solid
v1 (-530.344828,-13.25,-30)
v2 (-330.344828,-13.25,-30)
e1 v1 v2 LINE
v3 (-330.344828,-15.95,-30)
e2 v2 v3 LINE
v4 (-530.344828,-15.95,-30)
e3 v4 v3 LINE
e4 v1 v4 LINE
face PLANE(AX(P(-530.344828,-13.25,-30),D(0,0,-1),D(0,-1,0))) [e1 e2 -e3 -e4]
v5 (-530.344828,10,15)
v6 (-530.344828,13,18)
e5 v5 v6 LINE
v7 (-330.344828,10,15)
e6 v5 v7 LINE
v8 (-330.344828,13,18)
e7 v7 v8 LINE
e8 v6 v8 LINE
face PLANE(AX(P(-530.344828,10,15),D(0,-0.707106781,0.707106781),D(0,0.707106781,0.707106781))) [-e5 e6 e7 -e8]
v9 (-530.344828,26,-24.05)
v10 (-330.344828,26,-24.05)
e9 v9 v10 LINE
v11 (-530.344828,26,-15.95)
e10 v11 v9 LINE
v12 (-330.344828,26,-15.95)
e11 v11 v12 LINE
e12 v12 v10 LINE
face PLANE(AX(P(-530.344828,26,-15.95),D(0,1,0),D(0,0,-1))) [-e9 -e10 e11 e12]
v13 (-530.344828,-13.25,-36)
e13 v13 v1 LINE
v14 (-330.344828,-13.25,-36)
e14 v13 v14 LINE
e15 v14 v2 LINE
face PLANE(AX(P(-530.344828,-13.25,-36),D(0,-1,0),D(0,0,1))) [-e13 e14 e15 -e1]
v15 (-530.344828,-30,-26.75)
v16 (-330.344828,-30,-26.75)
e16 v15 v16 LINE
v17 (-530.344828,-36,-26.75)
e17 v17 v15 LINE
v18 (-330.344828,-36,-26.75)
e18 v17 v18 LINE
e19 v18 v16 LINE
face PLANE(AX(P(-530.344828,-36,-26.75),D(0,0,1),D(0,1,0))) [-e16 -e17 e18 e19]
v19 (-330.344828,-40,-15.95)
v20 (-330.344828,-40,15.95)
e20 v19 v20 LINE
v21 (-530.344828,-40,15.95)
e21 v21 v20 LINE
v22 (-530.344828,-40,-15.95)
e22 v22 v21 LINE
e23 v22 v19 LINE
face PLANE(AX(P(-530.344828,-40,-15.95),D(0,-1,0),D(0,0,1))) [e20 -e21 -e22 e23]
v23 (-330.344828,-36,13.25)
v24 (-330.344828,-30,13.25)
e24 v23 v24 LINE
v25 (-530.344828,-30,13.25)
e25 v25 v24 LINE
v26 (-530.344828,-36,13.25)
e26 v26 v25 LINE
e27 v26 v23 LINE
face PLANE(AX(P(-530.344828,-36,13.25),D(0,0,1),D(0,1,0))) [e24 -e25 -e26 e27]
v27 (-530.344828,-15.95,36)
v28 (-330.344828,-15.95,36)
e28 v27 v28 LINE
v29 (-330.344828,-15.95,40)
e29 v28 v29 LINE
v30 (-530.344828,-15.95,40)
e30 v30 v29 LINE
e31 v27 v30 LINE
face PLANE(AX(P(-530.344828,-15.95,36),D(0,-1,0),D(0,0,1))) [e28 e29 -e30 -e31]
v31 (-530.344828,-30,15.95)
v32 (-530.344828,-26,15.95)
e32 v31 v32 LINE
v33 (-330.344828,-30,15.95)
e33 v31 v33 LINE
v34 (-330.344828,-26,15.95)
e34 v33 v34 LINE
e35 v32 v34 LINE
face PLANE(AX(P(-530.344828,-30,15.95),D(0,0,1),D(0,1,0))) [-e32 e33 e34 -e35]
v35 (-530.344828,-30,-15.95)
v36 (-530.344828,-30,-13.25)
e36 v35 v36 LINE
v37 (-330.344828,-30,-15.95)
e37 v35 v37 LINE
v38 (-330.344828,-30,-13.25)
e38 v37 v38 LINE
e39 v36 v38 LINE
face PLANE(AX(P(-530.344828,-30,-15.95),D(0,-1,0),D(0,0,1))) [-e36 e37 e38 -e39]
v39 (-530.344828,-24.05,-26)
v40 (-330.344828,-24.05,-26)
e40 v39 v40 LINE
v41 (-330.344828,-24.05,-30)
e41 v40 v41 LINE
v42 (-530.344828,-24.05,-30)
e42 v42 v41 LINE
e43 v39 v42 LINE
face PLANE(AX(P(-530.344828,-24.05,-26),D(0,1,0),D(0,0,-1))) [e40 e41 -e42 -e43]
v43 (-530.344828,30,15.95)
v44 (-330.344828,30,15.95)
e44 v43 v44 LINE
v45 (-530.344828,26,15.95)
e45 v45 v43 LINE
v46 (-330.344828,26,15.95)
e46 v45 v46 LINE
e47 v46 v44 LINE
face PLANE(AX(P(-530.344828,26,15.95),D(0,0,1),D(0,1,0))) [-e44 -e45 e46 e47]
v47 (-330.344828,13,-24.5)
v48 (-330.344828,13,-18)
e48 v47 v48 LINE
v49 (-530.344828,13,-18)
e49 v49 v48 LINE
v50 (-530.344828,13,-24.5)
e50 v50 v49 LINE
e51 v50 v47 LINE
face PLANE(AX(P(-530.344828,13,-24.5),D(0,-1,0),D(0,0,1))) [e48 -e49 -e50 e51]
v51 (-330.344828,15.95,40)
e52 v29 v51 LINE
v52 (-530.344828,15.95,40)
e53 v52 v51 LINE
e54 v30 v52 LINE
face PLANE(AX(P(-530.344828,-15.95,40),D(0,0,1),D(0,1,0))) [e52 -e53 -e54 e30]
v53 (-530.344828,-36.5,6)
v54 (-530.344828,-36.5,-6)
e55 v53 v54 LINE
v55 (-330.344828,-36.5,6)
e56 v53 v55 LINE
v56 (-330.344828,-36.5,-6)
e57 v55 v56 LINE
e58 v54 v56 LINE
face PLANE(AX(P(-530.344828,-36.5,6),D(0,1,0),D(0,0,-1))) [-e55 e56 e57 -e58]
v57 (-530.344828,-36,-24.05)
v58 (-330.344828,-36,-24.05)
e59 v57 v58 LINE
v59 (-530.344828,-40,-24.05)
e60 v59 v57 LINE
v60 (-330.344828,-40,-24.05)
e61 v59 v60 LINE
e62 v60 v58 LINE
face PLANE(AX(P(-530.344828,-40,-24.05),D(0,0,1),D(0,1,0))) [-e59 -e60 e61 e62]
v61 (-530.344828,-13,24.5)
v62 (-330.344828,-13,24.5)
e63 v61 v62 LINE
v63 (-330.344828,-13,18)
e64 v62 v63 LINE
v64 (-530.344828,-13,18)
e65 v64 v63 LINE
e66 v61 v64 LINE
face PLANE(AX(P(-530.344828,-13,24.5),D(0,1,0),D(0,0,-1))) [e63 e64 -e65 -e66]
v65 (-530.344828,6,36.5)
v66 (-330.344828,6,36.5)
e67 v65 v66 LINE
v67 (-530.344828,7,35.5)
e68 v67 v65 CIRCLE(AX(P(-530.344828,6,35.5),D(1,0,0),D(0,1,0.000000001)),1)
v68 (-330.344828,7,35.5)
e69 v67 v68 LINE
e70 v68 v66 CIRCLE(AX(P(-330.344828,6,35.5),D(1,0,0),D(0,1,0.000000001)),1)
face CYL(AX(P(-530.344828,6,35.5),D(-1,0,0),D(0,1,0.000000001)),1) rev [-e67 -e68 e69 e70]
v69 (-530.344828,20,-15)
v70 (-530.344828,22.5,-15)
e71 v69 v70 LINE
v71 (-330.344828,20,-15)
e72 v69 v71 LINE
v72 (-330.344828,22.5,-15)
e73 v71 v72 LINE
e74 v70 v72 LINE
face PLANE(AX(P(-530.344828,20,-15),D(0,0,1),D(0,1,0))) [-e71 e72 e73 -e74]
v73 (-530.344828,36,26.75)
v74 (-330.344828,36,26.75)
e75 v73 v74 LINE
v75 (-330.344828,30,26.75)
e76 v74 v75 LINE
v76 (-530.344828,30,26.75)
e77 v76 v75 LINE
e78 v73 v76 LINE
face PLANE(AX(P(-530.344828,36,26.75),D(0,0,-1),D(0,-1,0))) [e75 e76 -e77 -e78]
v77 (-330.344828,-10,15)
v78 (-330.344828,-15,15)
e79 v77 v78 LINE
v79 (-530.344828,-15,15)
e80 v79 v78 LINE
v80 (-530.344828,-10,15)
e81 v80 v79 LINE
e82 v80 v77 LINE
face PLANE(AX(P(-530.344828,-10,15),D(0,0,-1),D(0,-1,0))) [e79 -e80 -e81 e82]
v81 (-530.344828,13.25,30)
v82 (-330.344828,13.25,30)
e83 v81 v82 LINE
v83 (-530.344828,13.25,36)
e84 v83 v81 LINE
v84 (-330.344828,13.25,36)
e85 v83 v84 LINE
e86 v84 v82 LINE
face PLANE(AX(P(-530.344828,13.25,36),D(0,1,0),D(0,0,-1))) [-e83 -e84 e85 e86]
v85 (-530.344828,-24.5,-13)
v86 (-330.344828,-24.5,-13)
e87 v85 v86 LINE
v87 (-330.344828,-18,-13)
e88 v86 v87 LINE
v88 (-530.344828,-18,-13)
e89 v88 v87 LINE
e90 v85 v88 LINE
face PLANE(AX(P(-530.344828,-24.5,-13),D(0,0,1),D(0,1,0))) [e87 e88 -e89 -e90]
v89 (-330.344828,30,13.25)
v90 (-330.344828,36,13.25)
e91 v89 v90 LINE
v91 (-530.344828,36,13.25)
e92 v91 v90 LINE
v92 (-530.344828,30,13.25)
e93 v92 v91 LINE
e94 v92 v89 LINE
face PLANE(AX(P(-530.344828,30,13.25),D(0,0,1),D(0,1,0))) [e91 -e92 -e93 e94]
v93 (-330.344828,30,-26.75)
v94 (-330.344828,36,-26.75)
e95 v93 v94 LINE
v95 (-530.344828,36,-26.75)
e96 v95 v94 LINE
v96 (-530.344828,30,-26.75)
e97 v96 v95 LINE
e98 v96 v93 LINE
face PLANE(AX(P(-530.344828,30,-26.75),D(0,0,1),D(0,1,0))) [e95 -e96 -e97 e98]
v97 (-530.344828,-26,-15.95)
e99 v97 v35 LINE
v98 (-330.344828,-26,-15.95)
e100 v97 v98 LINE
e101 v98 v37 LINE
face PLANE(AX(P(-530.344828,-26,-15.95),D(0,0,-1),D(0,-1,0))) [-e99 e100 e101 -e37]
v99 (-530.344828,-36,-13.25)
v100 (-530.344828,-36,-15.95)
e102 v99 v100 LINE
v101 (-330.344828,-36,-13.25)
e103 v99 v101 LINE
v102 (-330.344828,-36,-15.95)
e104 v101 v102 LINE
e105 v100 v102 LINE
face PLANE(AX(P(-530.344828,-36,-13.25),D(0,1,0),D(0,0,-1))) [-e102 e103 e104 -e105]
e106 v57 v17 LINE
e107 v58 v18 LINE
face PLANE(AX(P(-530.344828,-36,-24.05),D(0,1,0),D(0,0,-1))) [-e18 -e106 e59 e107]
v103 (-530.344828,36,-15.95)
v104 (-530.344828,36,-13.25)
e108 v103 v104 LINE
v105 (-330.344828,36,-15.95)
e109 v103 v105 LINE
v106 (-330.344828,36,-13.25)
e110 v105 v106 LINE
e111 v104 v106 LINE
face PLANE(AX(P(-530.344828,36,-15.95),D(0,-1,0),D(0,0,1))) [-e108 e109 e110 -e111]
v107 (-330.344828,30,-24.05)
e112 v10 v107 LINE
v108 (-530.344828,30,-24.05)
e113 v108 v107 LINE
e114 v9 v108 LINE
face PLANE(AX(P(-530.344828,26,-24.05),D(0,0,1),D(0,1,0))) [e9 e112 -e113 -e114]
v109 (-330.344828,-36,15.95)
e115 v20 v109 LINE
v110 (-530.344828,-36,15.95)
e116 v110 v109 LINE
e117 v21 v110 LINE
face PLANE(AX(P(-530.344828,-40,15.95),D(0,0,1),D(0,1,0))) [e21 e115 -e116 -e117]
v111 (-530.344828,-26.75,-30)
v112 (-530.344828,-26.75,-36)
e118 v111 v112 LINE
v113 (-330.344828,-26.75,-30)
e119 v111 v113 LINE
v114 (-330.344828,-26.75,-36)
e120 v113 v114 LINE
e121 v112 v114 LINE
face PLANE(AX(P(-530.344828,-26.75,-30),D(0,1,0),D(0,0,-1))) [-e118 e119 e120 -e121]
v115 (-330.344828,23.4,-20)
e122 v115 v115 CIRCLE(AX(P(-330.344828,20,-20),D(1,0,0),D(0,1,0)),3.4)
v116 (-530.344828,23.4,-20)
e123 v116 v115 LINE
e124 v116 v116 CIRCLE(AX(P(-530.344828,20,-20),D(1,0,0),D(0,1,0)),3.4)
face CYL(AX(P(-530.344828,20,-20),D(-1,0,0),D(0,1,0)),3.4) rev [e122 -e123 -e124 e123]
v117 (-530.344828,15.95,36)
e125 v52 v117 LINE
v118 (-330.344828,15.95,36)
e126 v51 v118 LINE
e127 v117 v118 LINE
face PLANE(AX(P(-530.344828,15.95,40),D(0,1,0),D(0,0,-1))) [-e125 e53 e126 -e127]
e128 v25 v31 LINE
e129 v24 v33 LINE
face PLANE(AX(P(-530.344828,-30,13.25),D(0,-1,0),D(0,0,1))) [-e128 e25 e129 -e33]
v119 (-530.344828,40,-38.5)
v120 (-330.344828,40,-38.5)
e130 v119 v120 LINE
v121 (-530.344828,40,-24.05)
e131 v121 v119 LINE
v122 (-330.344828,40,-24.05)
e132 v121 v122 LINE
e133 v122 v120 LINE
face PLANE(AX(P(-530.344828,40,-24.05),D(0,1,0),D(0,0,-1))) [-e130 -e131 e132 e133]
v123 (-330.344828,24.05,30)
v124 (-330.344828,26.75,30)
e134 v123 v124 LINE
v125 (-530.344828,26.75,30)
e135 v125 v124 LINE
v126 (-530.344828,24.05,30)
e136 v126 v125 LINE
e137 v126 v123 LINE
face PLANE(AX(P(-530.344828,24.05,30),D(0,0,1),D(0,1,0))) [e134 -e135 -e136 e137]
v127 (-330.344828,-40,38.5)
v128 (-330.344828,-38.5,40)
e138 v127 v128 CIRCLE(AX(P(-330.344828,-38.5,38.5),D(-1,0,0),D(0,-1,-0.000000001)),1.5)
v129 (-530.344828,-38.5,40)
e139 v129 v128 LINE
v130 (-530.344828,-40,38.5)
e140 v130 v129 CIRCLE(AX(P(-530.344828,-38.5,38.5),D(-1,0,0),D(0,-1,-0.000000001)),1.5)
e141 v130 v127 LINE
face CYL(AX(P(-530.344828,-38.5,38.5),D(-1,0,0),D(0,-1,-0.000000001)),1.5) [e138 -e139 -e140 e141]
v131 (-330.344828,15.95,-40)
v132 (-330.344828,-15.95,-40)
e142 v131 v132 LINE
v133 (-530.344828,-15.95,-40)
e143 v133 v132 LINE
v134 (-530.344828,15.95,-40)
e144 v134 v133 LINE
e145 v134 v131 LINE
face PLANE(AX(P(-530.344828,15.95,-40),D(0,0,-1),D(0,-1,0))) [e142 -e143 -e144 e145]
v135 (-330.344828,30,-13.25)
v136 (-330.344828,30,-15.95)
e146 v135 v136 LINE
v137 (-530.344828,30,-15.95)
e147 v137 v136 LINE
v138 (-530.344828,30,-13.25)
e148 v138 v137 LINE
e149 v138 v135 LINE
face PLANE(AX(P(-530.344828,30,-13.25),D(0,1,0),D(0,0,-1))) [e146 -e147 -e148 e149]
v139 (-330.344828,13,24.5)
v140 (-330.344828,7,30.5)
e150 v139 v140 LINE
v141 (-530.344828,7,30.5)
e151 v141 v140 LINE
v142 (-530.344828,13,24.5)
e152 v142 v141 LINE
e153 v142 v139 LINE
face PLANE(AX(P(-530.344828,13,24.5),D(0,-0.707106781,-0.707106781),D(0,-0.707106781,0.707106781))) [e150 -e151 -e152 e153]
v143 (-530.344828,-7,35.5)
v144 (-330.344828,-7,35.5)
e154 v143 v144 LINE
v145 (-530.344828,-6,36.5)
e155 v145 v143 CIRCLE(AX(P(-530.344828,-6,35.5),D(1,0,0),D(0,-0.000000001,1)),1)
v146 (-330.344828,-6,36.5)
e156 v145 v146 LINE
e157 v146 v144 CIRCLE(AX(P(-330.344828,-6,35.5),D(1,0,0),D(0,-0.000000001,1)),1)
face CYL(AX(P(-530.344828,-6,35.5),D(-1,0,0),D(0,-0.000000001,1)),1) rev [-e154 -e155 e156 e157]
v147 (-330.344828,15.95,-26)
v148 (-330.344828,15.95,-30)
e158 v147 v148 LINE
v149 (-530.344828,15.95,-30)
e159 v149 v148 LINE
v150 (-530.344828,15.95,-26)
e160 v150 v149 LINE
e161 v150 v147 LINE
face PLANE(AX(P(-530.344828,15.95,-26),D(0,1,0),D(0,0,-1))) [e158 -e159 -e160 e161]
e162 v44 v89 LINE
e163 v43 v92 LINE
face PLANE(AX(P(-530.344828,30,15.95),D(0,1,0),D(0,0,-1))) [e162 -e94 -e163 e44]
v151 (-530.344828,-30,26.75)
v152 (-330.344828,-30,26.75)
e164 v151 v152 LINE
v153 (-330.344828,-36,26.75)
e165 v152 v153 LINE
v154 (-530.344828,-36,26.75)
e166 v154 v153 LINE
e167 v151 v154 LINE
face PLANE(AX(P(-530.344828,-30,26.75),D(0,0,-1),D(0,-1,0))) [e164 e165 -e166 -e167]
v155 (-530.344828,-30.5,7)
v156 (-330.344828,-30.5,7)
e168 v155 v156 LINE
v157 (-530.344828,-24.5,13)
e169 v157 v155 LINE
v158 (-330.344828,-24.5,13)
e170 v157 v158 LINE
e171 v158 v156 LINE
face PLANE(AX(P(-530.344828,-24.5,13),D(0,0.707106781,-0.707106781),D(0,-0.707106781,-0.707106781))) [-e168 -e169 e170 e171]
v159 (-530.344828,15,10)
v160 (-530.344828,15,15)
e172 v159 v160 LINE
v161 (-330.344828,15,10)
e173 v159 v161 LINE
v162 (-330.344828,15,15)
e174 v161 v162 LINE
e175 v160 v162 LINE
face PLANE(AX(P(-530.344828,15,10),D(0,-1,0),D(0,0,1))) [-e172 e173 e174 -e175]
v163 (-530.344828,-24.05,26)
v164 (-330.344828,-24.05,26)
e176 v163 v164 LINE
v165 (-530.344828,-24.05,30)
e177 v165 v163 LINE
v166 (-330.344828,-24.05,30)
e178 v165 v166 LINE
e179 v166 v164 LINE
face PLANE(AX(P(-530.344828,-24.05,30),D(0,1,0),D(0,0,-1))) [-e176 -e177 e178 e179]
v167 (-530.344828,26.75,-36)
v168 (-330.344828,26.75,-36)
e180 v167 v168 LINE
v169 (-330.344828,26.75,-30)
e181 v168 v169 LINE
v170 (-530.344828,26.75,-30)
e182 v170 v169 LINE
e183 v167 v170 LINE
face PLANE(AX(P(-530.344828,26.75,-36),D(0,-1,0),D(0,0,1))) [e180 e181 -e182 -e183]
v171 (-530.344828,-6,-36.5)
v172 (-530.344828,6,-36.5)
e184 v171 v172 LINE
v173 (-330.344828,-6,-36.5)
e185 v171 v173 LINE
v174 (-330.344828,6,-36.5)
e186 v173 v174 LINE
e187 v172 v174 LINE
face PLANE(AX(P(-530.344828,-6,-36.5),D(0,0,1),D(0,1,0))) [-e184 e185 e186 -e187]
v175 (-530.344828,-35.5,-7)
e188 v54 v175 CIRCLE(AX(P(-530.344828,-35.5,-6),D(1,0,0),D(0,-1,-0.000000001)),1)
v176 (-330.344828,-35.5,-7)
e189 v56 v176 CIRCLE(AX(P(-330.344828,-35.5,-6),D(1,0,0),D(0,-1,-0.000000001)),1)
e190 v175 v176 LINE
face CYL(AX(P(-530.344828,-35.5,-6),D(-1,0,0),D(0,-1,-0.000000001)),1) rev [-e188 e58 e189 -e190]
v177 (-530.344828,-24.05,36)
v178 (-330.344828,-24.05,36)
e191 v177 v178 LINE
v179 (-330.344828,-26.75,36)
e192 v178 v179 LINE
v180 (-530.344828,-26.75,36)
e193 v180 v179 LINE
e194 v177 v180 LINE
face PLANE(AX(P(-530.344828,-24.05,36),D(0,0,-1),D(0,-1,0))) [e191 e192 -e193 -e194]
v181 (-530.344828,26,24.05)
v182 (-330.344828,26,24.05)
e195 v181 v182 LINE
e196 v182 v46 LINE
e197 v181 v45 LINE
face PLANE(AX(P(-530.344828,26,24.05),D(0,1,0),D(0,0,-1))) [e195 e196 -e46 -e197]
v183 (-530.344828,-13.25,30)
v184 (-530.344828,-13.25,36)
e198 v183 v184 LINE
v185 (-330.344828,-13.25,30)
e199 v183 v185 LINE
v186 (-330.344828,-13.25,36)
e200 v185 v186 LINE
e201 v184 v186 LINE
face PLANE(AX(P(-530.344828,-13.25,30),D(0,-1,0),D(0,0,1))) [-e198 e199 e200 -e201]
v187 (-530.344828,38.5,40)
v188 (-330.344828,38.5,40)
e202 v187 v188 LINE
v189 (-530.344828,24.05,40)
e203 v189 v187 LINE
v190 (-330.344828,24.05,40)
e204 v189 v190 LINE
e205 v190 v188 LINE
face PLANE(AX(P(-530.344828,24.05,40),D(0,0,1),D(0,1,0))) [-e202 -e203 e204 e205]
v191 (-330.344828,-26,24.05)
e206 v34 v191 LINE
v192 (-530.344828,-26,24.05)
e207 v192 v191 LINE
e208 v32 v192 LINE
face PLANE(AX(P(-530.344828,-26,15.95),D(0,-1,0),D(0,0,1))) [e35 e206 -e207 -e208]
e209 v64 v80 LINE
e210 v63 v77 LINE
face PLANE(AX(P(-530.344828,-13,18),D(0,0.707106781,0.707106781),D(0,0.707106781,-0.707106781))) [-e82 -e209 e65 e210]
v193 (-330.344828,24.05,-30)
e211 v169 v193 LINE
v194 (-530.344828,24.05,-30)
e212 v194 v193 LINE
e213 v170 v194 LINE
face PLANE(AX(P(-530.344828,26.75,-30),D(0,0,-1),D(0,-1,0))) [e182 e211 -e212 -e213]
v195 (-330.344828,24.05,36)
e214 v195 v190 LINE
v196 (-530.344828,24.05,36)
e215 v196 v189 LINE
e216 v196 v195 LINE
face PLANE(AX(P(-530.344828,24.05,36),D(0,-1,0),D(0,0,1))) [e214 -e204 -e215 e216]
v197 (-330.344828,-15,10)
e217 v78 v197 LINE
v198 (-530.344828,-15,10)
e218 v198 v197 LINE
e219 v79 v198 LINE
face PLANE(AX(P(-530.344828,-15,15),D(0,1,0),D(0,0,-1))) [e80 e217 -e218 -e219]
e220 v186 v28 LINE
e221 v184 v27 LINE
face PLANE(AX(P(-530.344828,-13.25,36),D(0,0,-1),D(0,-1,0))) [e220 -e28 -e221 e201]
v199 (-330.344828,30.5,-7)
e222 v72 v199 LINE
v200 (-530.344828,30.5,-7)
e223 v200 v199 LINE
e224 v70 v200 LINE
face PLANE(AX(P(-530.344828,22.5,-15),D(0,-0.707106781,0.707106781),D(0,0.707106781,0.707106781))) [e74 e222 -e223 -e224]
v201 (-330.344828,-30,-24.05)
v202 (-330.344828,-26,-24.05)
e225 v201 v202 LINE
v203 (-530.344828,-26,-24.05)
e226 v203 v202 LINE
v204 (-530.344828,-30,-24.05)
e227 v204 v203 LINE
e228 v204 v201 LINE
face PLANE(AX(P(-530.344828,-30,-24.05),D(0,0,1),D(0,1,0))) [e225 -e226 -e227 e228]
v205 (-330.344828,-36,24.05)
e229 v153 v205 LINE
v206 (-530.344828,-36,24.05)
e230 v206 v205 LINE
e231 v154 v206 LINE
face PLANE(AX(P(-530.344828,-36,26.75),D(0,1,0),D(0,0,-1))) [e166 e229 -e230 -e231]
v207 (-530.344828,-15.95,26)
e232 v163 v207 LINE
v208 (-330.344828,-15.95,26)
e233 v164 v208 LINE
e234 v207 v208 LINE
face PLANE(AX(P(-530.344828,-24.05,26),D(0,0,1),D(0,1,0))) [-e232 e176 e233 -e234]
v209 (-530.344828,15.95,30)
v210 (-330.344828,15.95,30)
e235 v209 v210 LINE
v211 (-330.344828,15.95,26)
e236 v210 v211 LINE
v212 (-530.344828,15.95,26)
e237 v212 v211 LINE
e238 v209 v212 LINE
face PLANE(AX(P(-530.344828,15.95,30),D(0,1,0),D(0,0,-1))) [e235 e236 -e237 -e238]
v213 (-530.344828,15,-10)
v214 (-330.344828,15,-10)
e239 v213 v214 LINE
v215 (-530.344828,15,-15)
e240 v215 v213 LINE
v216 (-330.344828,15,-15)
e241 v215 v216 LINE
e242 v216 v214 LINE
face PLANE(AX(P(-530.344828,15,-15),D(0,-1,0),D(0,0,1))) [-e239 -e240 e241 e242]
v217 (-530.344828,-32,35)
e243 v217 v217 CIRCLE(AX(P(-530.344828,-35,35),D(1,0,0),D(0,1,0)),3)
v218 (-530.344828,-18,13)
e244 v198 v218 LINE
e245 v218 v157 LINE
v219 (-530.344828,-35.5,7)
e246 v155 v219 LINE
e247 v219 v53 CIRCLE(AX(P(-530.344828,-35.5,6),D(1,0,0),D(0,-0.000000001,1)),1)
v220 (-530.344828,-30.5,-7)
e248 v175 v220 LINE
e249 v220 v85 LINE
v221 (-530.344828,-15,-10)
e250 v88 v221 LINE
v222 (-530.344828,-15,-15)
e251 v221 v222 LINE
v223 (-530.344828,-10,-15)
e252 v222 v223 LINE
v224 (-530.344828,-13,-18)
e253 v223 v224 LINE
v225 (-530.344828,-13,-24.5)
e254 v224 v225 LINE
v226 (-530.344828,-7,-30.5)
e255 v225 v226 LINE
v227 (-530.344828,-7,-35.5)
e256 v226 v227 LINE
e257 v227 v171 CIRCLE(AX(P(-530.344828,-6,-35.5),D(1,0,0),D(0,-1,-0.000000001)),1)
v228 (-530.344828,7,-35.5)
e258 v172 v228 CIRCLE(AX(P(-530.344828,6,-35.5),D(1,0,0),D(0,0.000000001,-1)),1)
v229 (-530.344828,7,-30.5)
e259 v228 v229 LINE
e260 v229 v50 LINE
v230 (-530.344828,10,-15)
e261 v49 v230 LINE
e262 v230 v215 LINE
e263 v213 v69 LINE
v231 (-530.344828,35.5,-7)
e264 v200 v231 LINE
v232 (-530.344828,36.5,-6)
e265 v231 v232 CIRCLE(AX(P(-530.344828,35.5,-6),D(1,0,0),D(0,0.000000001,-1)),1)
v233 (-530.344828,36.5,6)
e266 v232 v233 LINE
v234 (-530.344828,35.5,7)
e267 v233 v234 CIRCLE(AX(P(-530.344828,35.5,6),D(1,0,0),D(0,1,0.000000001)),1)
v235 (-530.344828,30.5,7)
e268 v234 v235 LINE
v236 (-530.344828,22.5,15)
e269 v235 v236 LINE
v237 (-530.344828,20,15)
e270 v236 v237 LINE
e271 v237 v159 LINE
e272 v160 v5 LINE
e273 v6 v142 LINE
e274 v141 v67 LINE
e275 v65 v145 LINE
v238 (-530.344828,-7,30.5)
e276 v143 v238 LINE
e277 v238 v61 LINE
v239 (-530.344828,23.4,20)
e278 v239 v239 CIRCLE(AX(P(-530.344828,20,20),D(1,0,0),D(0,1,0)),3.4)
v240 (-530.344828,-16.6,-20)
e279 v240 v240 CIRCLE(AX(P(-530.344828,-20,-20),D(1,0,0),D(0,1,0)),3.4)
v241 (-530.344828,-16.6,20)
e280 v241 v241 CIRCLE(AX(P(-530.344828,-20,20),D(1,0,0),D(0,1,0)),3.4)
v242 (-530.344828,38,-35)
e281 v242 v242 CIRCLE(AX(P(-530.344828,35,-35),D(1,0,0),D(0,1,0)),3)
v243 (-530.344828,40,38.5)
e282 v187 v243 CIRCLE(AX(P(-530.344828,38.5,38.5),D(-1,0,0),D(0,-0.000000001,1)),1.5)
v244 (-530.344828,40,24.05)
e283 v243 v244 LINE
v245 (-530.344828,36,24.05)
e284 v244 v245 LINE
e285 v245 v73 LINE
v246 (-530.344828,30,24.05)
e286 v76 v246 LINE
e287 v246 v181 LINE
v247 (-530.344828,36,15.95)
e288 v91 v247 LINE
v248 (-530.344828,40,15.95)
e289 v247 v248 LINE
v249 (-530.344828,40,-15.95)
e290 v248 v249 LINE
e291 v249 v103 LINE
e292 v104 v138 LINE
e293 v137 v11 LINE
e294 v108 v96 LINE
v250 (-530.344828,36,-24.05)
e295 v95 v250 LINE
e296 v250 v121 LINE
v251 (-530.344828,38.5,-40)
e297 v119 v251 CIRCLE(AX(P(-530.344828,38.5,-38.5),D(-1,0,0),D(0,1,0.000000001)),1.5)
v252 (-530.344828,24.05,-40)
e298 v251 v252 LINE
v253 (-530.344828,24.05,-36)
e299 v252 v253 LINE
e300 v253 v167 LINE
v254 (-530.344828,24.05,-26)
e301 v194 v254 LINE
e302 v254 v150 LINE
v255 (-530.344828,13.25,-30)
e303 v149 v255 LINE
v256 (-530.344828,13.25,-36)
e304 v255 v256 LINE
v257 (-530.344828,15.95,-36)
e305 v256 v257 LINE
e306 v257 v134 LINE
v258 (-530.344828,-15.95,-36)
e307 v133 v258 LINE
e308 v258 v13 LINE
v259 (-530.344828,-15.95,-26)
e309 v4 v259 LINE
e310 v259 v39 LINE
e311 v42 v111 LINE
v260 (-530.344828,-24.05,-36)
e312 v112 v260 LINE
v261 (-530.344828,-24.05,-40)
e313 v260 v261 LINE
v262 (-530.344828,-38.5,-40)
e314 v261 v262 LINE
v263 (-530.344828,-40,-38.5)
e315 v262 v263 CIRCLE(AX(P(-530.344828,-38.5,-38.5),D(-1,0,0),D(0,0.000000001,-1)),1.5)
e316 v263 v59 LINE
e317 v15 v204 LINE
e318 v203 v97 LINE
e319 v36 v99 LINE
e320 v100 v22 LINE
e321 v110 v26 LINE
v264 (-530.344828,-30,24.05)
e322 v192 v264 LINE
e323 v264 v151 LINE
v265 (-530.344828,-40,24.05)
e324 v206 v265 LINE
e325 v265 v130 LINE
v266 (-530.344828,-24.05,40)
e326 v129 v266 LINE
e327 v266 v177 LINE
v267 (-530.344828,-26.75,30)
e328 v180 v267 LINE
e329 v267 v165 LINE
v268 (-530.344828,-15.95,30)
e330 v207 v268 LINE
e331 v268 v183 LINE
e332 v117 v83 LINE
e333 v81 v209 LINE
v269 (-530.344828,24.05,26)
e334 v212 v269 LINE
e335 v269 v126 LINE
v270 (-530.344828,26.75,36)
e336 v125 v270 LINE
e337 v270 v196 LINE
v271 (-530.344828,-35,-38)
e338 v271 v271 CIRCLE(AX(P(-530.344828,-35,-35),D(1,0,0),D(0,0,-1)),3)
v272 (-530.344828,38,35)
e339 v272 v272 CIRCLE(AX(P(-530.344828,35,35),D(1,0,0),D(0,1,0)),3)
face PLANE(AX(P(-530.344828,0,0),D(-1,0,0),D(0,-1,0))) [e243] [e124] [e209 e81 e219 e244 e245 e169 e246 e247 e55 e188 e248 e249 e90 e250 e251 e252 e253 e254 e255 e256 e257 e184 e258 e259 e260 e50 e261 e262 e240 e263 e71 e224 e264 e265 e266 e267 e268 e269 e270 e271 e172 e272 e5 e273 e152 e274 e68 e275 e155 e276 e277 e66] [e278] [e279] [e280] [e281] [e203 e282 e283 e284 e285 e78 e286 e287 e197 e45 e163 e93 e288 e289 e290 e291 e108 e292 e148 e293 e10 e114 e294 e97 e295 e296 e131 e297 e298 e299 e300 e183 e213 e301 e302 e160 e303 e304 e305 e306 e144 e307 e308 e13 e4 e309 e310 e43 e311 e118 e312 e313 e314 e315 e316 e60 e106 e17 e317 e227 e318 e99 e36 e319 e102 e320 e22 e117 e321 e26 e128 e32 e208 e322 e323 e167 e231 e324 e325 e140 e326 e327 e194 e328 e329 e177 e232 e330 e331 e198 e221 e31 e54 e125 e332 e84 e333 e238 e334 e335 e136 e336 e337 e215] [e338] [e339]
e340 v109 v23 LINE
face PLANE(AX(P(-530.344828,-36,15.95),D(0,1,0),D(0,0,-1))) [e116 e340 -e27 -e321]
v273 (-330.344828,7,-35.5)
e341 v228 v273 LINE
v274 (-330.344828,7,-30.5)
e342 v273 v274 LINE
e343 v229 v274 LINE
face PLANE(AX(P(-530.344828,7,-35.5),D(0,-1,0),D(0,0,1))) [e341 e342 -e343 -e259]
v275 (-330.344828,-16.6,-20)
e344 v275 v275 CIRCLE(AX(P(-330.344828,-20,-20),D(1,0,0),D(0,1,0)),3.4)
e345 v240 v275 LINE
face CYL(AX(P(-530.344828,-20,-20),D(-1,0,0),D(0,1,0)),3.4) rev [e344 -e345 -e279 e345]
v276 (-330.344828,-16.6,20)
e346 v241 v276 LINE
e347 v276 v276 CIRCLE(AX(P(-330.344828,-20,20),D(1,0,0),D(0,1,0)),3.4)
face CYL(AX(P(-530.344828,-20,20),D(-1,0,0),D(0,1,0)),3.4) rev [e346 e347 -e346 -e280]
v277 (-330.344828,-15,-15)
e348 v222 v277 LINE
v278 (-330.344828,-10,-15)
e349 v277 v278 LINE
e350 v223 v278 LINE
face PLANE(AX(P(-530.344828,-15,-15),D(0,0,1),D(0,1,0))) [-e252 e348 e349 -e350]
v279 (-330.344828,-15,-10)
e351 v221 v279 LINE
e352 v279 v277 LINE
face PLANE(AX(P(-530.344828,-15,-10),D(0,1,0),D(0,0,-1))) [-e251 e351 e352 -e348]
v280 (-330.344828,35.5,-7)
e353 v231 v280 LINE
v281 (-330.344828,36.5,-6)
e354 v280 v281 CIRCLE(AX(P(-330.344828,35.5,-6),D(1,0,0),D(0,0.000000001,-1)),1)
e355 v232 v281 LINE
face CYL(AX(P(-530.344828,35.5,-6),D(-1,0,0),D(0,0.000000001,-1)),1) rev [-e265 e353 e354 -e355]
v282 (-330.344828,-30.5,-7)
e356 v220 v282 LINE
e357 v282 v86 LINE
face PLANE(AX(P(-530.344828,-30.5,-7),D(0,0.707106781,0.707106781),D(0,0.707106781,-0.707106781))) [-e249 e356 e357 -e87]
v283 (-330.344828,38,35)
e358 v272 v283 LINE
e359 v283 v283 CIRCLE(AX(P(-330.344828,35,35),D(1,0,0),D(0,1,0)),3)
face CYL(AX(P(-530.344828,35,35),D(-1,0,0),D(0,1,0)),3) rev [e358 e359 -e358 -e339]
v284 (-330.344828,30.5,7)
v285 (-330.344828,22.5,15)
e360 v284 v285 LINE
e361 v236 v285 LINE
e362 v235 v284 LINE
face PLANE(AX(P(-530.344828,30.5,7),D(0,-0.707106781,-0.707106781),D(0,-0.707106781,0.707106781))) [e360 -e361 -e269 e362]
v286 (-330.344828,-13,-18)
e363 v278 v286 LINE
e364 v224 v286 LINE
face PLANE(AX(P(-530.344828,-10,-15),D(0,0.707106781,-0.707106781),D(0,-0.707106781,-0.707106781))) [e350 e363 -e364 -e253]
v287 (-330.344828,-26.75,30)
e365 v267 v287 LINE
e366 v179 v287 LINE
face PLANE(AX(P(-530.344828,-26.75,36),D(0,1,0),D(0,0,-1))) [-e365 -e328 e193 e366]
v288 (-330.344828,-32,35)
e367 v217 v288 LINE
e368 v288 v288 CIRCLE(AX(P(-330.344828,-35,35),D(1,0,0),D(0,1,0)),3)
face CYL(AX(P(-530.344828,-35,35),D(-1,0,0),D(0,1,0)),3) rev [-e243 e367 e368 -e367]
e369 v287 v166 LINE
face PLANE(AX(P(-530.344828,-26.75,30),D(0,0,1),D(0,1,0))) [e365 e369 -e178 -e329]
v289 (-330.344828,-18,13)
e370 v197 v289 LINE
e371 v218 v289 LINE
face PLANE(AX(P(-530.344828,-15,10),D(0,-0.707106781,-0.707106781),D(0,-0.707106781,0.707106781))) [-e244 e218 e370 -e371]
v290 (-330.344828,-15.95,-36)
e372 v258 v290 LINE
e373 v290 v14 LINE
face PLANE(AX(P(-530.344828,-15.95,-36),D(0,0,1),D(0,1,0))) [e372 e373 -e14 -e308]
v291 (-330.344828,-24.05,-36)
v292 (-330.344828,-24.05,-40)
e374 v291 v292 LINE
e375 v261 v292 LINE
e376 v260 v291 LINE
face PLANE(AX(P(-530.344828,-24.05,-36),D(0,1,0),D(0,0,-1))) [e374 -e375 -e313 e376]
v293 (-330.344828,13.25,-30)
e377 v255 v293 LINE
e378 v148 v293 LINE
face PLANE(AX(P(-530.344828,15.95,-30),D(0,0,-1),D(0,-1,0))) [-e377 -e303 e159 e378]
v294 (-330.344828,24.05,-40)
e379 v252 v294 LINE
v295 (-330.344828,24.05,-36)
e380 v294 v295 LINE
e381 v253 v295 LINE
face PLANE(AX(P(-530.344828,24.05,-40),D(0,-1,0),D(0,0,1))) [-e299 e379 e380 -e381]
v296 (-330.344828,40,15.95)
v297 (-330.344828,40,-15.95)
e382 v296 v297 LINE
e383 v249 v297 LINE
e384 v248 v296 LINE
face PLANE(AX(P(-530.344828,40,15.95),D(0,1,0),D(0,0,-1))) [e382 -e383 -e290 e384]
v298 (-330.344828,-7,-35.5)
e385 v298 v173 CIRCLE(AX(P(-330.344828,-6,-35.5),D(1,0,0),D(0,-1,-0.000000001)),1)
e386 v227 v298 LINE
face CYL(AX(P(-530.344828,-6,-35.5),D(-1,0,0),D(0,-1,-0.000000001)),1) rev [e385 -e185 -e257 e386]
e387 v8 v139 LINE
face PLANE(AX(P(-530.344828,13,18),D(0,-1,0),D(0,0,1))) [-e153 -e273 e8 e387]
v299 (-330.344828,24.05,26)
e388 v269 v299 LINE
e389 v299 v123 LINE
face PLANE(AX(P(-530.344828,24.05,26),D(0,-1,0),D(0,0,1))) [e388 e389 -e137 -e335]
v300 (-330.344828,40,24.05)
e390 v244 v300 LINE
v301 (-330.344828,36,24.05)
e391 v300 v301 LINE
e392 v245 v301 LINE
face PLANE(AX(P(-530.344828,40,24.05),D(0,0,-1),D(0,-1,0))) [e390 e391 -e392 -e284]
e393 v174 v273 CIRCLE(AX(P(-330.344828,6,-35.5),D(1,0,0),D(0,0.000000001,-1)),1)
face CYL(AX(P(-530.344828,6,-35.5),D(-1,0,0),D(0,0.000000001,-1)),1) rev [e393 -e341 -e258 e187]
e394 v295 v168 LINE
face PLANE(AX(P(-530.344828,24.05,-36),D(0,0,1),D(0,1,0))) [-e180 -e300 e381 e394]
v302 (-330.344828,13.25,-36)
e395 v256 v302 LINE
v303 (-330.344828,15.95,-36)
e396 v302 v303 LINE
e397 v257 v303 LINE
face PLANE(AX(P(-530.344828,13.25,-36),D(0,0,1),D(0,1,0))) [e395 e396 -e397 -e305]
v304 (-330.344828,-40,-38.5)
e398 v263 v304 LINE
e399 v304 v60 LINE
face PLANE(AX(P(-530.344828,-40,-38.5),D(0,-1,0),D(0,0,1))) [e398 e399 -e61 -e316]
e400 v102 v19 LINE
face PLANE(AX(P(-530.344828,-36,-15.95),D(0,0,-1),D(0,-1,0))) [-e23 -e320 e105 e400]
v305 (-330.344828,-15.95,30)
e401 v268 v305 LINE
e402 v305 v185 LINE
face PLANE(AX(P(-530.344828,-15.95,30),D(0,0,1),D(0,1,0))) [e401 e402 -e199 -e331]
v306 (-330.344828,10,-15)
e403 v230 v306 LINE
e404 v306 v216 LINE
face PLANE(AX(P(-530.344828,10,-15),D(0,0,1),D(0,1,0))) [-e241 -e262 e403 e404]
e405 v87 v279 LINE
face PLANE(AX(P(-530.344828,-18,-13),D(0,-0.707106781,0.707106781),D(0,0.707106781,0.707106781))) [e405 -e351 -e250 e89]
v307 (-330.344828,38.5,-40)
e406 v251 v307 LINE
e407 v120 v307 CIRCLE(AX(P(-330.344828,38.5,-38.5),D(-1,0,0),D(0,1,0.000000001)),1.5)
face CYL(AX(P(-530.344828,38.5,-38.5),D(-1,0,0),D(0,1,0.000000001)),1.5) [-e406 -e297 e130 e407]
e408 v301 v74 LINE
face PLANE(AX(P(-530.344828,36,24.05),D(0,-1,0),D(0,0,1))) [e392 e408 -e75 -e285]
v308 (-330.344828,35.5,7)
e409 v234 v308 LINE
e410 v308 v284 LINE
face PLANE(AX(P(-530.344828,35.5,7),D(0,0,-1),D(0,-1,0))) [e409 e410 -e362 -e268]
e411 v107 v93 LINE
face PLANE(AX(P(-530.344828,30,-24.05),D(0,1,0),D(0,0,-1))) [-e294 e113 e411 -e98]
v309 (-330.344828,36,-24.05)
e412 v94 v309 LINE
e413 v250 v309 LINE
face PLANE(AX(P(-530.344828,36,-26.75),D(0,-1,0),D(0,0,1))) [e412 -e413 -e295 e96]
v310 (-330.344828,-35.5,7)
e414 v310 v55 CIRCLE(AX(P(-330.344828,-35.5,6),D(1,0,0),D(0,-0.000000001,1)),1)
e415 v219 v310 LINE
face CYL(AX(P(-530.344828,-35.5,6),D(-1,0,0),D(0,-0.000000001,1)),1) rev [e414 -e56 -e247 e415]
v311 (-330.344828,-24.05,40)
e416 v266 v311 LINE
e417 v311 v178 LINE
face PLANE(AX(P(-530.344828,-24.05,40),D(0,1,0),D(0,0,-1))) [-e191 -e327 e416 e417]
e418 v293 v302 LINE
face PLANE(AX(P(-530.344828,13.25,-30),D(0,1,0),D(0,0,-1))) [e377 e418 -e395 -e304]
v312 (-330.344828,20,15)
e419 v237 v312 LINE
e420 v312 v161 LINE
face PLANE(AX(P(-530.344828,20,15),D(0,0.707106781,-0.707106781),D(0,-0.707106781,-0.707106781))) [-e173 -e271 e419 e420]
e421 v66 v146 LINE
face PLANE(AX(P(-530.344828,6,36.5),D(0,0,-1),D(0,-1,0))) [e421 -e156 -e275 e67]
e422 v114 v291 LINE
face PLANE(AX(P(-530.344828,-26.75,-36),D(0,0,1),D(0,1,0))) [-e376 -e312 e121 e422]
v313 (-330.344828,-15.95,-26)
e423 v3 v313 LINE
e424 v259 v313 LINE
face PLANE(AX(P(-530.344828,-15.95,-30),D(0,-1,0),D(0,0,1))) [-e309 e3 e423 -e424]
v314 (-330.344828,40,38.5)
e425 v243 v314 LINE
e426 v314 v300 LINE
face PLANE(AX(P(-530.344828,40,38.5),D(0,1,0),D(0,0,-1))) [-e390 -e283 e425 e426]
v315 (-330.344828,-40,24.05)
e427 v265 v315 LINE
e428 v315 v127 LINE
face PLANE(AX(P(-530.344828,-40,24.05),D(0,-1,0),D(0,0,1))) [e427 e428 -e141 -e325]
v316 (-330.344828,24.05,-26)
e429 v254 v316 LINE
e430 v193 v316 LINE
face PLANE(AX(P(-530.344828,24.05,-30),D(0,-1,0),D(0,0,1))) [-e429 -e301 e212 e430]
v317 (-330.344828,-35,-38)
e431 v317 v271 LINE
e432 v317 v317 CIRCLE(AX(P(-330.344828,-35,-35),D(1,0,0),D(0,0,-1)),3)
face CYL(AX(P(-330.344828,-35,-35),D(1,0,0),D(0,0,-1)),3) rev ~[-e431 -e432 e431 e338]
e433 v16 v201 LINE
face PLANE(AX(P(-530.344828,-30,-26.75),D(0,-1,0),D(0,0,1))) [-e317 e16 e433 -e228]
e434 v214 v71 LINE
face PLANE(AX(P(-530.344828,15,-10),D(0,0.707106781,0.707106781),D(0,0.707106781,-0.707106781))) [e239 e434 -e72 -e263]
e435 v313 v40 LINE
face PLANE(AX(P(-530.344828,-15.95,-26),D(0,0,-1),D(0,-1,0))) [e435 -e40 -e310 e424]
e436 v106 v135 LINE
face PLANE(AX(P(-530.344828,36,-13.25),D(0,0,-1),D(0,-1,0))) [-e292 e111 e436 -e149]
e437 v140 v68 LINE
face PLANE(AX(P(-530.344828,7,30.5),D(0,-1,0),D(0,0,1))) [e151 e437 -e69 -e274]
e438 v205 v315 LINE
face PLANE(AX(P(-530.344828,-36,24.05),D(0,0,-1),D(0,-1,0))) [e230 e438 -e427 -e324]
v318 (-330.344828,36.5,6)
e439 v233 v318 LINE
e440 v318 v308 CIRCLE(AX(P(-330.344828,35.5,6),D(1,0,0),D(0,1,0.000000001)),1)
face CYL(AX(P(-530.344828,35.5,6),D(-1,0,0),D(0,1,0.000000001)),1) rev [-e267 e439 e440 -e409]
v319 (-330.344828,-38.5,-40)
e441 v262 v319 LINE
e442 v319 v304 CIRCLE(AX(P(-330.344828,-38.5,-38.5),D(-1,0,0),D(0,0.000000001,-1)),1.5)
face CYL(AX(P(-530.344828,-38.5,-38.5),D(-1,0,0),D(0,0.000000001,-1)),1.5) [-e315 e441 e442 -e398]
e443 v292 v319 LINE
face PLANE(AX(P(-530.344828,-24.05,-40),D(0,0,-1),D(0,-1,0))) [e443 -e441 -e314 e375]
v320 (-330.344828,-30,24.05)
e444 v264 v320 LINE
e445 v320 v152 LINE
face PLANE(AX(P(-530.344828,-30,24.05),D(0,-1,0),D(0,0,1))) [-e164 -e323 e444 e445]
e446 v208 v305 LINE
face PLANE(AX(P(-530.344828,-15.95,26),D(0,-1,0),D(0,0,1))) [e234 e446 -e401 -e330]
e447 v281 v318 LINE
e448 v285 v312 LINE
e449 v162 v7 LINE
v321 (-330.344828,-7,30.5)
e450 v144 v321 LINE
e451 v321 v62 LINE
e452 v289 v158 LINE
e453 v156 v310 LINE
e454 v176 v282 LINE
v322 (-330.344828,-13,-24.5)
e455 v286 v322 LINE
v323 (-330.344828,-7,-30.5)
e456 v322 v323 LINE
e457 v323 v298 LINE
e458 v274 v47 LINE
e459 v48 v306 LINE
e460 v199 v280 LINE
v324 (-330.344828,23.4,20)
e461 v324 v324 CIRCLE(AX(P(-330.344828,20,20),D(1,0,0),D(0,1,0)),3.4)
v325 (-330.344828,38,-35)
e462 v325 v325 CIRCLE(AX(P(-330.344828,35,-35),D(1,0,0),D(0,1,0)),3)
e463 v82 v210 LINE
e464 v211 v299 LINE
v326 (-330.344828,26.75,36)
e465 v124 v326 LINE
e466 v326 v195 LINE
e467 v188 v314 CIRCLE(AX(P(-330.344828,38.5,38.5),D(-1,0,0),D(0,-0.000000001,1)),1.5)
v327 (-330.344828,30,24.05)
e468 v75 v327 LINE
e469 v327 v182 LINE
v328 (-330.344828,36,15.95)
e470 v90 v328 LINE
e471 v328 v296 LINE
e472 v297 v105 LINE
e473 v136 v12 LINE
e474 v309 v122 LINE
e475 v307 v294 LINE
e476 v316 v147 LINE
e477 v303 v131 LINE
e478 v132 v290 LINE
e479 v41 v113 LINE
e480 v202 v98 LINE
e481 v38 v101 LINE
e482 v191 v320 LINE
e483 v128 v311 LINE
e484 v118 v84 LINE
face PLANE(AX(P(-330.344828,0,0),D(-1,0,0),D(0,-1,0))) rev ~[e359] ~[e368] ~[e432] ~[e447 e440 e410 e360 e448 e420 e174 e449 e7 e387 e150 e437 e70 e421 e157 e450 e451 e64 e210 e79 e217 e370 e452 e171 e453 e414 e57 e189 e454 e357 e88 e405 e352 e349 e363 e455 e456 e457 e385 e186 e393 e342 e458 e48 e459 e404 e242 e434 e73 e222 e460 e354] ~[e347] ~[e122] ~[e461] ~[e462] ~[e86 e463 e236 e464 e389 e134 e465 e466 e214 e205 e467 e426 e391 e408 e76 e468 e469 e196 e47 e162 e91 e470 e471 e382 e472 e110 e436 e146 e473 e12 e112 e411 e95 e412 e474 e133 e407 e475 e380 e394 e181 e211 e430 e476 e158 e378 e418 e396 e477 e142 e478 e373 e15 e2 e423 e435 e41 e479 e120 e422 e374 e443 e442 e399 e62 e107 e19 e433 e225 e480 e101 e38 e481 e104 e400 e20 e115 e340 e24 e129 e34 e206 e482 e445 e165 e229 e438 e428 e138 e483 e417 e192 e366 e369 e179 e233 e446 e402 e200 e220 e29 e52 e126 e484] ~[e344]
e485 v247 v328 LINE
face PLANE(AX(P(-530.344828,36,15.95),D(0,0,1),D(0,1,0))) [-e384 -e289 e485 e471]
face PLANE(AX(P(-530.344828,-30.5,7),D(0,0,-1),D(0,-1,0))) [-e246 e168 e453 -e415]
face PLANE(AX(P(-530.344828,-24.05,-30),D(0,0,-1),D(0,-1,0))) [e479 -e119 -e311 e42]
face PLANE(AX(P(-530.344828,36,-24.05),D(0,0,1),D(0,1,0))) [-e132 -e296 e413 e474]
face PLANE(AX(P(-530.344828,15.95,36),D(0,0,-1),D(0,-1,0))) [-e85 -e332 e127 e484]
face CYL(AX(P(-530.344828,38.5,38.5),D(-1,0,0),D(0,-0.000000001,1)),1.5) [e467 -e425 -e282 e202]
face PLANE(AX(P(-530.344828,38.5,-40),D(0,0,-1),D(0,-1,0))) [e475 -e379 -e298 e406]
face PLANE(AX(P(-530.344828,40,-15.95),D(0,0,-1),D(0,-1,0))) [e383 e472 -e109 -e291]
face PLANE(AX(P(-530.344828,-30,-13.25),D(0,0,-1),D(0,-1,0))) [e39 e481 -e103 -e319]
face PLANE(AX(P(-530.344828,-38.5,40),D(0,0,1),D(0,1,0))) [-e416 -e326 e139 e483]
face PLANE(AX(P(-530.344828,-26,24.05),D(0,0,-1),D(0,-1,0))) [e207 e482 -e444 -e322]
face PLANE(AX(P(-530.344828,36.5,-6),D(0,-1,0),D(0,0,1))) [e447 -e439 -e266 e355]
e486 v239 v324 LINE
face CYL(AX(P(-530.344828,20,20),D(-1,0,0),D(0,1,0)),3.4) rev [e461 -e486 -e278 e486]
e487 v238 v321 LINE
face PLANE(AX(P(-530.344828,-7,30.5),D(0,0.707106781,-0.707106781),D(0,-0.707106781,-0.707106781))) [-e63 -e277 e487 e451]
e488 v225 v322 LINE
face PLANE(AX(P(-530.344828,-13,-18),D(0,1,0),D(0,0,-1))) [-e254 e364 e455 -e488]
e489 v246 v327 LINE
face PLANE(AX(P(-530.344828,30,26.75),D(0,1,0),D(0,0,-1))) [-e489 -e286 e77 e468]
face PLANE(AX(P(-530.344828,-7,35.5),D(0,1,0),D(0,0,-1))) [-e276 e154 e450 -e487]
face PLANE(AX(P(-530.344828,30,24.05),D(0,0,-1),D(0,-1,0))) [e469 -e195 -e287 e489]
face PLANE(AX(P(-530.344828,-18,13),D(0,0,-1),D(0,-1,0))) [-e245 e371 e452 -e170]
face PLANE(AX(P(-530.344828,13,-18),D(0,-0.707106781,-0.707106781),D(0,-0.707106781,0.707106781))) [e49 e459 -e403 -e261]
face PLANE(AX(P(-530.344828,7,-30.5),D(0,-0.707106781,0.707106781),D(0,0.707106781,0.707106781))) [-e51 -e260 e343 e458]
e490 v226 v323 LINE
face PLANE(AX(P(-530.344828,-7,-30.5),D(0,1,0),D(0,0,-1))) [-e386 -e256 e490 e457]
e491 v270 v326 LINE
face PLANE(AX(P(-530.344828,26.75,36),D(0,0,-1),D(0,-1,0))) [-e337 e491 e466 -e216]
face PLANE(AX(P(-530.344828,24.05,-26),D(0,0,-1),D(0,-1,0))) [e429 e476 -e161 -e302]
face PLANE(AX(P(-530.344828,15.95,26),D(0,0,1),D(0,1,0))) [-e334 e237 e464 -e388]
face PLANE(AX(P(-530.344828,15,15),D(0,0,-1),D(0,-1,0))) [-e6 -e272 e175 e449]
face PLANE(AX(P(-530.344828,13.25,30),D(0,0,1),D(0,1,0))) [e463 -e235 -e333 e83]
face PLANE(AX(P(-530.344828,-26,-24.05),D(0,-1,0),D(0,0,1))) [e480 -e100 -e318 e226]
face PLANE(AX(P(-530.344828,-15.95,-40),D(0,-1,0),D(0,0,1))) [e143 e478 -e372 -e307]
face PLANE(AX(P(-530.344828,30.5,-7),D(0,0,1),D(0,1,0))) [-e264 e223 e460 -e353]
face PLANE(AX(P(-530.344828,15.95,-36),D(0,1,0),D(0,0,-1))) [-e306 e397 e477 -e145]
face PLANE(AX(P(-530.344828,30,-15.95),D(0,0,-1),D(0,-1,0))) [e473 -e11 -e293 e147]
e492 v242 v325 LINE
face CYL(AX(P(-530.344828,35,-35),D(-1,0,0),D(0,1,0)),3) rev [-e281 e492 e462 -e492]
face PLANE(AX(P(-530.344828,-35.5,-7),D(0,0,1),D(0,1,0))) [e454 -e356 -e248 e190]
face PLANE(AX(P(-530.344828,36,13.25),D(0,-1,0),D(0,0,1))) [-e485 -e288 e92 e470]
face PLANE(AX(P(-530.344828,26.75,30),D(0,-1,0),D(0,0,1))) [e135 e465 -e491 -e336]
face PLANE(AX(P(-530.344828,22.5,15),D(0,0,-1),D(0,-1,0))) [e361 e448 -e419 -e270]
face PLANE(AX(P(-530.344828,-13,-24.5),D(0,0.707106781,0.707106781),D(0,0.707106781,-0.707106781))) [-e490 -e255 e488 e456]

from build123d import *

# Parameters (mm, degrees)
SKETCH1_R                                 = 3.4
SKETCH1_R_2                               = 3
ALUMINIUM_PROFILE_80_X_80G_X_R1_5_1_DEPTH = 200
SKETCH10_R                                = 3
CUT_EXTRUDE1_DEPTH                        = 208.846096908


with BuildPart() as part:
    # Sketch1 → Aluminium profile 80 X 80G X R1.5(1) (new body)
    with BuildSketch(Plane.YZ.offset(-530.344827586)):
        with BuildLine():
            Line((-24.05, 40), (-24.05, 36))
            Line((-24.05, 36), (-26.75, 36))
            Line((-26.75, 36), (-26.75, 30))
            Line((-26.75, 30), (-24.05, 30))
            Line((-24.05, 30), (-24.05, 26))
            Line((-24.05, 26), (-15.95, 26))
            Line((-15.95, 26), (-15.95, 30))
            Line((-15.95, 30), (-13.25, 30))
            Line((-13.25, 30), (-13.25, 36))
            Line((-13.25, 36), (-15.95, 36))
            Line((-15.95, 36), (-15.95, 40))
            Line((-15.95, 40), (15.95, 40))
            Line((15.95, 40), (15.95, 36))
            Line((15.95, 36), (13.25, 36))
            Line((13.25, 36), (13.25, 30))
            Line((13.25, 30), (15.95, 30))
            Line((15.95, 30), (15.95, 26))
            Line((15.95, 26), (24.05, 26))
            Line((24.05, 26), (24.05, 30))
            Line((24.05, 30), (26.75, 30))
            Line((26.75, 30), (26.75, 36))
            Line((26.75, 36), (24.05, 36))
            Line((24.05, 36), (24.05, 40))
            Line((24.05, 40), (38.5, 40))
            ThreePointArc((38.5, 40), (39.560660172, 39.560660172), (40, 38.5))
            Line((40, 38.5), (40, 24.05))
            Line((40, 24.05), (36, 24.05))
            Line((36, 24.05), (36, 26.75))
            Line((36, 26.75), (30, 26.75))
            Line((30, 26.75), (30, 24.05))
            Line((30, 24.05), (26, 24.05))
            Line((26, 24.05), (26, 15.95))
            Line((26, 15.95), (30, 15.95))
            Line((30, 15.95), (30, 13.25))
            Line((30, 13.25), (36, 13.25))
            Line((36, 13.25), (36, 15.95))
            Line((36, 15.95), (40, 15.95))
            Line((40, 15.95), (40, -15.95))
            Line((40, -15.95), (36, -15.95))
            Line((36, -15.95), (36, -13.25))
            Line((36, -13.25), (30, -13.25))
            Line((30, -13.25), (30, -15.95))
            Line((30, -15.95), (26, -15.95))
            Line((26, -15.95), (26, -24.05))
            Line((26, -24.05), (30, -24.05))
            Line((30, -24.05), (30, -26.75))
            Line((30, -26.75), (36, -26.75))
            Line((36, -26.75), (36, -24.05))
            Line((36, -24.05), (40, -24.05))
            Line((40, -24.05), (40, -38.5))
            ThreePointArc((40, -38.5), (39.560660172, -39.560660172), (38.5, -40))
            Line((38.5, -40), (24.05, -40))
            Line((24.05, -40), (24.05, -36))
            Line((24.05, -36), (26.75, -36))
            Line((26.75, -36), (26.75, -30))
            Line((26.75, -30), (24.05, -30))
            Line((24.05, -30), (24.05, -26))
            Line((24.05, -26), (15.95, -26))
            Line((15.95, -26), (15.95, -30))
            Line((15.95, -30), (13.25, -30))
            Line((13.25, -30), (13.25, -36))
            Line((13.25, -36), (15.95, -36))
            Line((15.95, -36), (15.95, -40))
            Line((15.95, -40), (-15.95, -40))
            Line((-15.95, -40), (-15.95, -36))
            Line((-15.95, -36), (-13.25, -36))
            Line((-13.25, -36), (-13.25, -30))
            Line((-13.25, -30), (-15.95, -30))
            Line((-15.95, -30), (-15.95, -26))
            Line((-15.95, -26), (-24.05, -26))
            Line((-24.05, -26), (-24.05, -30))
            Line((-24.05, -30), (-26.75, -30))
            Line((-26.75, -30), (-26.75, -36))
            Line((-26.75, -36), (-24.05, -36))
            Line((-24.05, -36), (-24.05, -40))
            Line((-24.05, -40), (-38.5, -40))
            ThreePointArc((-38.5, -40), (-39.560660172, -39.560660172), (-40, -38.5))
            Line((-40, -38.5), (-40, -24.05))
            Line((-40, -24.05), (-36, -24.05))
            Line((-36, -24.05), (-36, -26.75))
            Line((-36, -26.75), (-30, -26.75))
            Line((-30, -26.75), (-30, -24.05))
            Line((-30, -24.05), (-26, -24.05))
            Line((-26, -24.05), (-26, -15.95))
            Line((-26, -15.95), (-30, -15.95))
            Line((-30, -15.95), (-30, -13.25))
            Line((-30, -13.25), (-36, -13.25))
            Line((-36, -13.25), (-36, -15.95))
            Line((-36, -15.95), (-40, -15.95))
            Line((-40, -15.95), (-40, 15.95))
            Line((-40, 15.95), (-36, 15.95))
            Line((-36, 15.95), (-36, 13.25))
            Line((-36, 13.25), (-30, 13.25))
            Line((-30, 13.25), (-30, 15.95))
            Line((-30, 15.95), (-26, 15.95))
            Line((-26, 15.95), (-26, 24.05))
            Line((-26, 24.05), (-30, 24.05))
            Line((-30, 24.05), (-30, 26.75))
            Line((-30, 26.75), (-36, 26.75))
            Line((-36, 26.75), (-36, 24.05))
            Line((-36, 24.05), (-40, 24.05))
            Line((-40, 24.05), (-40, 38.5))
            ThreePointArc((-40, 38.5), (-39.560660172, 39.560660172), (-38.5, 40))
            Line((-38.5, 40), (-24.05, 40))
        make_face()
        with Locations((-20, 20)):
            Circle(SKETCH1_R, mode=Mode.SUBTRACT)
        with Locations((20, 20)):
            Circle(SKETCH1_R, mode=Mode.SUBTRACT)
        with Locations((20, -20)):
            Circle(SKETCH1_R, mode=Mode.SUBTRACT)
        with Locations((-20, -20)):
            Circle(SKETCH1_R, mode=Mode.SUBTRACT)
        with Locations((-35, 35)):
            Circle(SKETCH1_R_2, mode=Mode.SUBTRACT)
        with Locations((35, 35)):
            Circle(SKETCH1_R_2, mode=Mode.SUBTRACT)
        with Locations((35, -35)):
            Circle(SKETCH1_R_2, mode=Mode.SUBTRACT)
        with BuildLine():
            Line((-13, 18), (-10, 15))
            Line((-10, 15), (-15, 15))
            Line((-15, 15), (-15, 10))
            Line((-15, 10), (-18, 13))
            Line((-18, 13), (-24.5, 13))
            Line((-24.5, 13), (-30.5, 7))
            Line((-30.5, 7), (-35.5, 7))
            ThreePointArc((-35.5, 7), (-36.207106781, 6.707106781), (-36.5, 6))
            Line((-36.5, 6), (-36.5, -6))
            ThreePointArc((-36.5, -6), (-36.207106781, -6.707106781), (-35.5, -7))
            Line((-35.5, -7), (-30.5, -7))
            Line((-30.5, -7), (-24.5, -13))
            Line((-24.5, -13), (-18, -13))
            Line((-18, -13), (-15, -10))
            Line((-15, -10), (-15, -15))
            Line((-15, -15), (-10, -15))
            Line((-10, -15), (-13, -18))
            Line((-13, -18), (-13, -24.5))
            Line((-13, -24.5), (-7, -30.5))
            Line((-7, -30.5), (-7, -35.5))
            ThreePointArc((-7, -35.5), (-6.707106781, -36.207106781), (-6, -36.5))
            Line((-6, -36.5), (6, -36.5))
            ThreePointArc((6, -36.5), (6.707106781, -36.207106781), (7, -35.5))
            Line((7, -35.5), (7, -30.5))
            Line((7, -30.5), (13, -24.5))
            Line((13, -24.5), (13, -18))
            Line((13, -18), (10, -15))
            Line((10, -15), (15, -15))
            Line((15, -15), (15, -10))
            Line((15, -10), (20, -15))
            Line((20, -15), (22.5, -15))
            Line((22.5, -15), (30.5, -7))
            Line((30.5, -7), (35.5, -7))
            ThreePointArc((35.5, -7), (36.207106781, -6.707106781), (36.5, -6))
            Line((36.5, -6), (36.5, 6))
            ThreePointArc((36.5, 6), (36.207106781, 6.707106781), (35.5, 7))
            Line((35.5, 7), (30.5, 7))
            Line((30.5, 7), (22.5, 15))
            Line((22.5, 15), (20, 15))
            Line((20, 15), (15, 10))
            Line((15, 10), (15, 15))
            Line((15, 15), (10, 15))
            Line((10, 15), (13, 18))
            Line((13, 18), (13, 24.5))
            Line((13, 24.5), (7, 30.5))
            Line((7, 30.5), (7, 35.5))
            ThreePointArc((7, 35.5), (6.707106781, 36.207106781), (6, 36.5))
            Line((6, 36.5), (-6, 36.5))
            ThreePointArc((-6, 36.5), (-6.707106781, 36.207106781), (-7, 35.5))
            Line((-7, 35.5), (-7, 30.5))
            Line((-7, 30.5), (-13, 24.5))
            Line((-13, 24.5), (-13, 18))
        make_face(mode=Mode.SUBTRACT)
    extrude(amount=ALUMINIUM_PROFILE_80_X_80G_X_R1_5_1_DEPTH)

    # Sketch10 → Cut-Extrude1 (cut, through all)
    with BuildSketch(Plane(origin=(-330.344827586, 0, 0), x_dir=(0, 0, -1), z_dir=(1, 0, 0))):
        with Locations((35, -35)):
            Circle(SKETCH10_R)
    extrude(amount=-CUT_EXTRUDE1_DEPTH, mode=Mode.SUBTRACT)


solid = part.part
